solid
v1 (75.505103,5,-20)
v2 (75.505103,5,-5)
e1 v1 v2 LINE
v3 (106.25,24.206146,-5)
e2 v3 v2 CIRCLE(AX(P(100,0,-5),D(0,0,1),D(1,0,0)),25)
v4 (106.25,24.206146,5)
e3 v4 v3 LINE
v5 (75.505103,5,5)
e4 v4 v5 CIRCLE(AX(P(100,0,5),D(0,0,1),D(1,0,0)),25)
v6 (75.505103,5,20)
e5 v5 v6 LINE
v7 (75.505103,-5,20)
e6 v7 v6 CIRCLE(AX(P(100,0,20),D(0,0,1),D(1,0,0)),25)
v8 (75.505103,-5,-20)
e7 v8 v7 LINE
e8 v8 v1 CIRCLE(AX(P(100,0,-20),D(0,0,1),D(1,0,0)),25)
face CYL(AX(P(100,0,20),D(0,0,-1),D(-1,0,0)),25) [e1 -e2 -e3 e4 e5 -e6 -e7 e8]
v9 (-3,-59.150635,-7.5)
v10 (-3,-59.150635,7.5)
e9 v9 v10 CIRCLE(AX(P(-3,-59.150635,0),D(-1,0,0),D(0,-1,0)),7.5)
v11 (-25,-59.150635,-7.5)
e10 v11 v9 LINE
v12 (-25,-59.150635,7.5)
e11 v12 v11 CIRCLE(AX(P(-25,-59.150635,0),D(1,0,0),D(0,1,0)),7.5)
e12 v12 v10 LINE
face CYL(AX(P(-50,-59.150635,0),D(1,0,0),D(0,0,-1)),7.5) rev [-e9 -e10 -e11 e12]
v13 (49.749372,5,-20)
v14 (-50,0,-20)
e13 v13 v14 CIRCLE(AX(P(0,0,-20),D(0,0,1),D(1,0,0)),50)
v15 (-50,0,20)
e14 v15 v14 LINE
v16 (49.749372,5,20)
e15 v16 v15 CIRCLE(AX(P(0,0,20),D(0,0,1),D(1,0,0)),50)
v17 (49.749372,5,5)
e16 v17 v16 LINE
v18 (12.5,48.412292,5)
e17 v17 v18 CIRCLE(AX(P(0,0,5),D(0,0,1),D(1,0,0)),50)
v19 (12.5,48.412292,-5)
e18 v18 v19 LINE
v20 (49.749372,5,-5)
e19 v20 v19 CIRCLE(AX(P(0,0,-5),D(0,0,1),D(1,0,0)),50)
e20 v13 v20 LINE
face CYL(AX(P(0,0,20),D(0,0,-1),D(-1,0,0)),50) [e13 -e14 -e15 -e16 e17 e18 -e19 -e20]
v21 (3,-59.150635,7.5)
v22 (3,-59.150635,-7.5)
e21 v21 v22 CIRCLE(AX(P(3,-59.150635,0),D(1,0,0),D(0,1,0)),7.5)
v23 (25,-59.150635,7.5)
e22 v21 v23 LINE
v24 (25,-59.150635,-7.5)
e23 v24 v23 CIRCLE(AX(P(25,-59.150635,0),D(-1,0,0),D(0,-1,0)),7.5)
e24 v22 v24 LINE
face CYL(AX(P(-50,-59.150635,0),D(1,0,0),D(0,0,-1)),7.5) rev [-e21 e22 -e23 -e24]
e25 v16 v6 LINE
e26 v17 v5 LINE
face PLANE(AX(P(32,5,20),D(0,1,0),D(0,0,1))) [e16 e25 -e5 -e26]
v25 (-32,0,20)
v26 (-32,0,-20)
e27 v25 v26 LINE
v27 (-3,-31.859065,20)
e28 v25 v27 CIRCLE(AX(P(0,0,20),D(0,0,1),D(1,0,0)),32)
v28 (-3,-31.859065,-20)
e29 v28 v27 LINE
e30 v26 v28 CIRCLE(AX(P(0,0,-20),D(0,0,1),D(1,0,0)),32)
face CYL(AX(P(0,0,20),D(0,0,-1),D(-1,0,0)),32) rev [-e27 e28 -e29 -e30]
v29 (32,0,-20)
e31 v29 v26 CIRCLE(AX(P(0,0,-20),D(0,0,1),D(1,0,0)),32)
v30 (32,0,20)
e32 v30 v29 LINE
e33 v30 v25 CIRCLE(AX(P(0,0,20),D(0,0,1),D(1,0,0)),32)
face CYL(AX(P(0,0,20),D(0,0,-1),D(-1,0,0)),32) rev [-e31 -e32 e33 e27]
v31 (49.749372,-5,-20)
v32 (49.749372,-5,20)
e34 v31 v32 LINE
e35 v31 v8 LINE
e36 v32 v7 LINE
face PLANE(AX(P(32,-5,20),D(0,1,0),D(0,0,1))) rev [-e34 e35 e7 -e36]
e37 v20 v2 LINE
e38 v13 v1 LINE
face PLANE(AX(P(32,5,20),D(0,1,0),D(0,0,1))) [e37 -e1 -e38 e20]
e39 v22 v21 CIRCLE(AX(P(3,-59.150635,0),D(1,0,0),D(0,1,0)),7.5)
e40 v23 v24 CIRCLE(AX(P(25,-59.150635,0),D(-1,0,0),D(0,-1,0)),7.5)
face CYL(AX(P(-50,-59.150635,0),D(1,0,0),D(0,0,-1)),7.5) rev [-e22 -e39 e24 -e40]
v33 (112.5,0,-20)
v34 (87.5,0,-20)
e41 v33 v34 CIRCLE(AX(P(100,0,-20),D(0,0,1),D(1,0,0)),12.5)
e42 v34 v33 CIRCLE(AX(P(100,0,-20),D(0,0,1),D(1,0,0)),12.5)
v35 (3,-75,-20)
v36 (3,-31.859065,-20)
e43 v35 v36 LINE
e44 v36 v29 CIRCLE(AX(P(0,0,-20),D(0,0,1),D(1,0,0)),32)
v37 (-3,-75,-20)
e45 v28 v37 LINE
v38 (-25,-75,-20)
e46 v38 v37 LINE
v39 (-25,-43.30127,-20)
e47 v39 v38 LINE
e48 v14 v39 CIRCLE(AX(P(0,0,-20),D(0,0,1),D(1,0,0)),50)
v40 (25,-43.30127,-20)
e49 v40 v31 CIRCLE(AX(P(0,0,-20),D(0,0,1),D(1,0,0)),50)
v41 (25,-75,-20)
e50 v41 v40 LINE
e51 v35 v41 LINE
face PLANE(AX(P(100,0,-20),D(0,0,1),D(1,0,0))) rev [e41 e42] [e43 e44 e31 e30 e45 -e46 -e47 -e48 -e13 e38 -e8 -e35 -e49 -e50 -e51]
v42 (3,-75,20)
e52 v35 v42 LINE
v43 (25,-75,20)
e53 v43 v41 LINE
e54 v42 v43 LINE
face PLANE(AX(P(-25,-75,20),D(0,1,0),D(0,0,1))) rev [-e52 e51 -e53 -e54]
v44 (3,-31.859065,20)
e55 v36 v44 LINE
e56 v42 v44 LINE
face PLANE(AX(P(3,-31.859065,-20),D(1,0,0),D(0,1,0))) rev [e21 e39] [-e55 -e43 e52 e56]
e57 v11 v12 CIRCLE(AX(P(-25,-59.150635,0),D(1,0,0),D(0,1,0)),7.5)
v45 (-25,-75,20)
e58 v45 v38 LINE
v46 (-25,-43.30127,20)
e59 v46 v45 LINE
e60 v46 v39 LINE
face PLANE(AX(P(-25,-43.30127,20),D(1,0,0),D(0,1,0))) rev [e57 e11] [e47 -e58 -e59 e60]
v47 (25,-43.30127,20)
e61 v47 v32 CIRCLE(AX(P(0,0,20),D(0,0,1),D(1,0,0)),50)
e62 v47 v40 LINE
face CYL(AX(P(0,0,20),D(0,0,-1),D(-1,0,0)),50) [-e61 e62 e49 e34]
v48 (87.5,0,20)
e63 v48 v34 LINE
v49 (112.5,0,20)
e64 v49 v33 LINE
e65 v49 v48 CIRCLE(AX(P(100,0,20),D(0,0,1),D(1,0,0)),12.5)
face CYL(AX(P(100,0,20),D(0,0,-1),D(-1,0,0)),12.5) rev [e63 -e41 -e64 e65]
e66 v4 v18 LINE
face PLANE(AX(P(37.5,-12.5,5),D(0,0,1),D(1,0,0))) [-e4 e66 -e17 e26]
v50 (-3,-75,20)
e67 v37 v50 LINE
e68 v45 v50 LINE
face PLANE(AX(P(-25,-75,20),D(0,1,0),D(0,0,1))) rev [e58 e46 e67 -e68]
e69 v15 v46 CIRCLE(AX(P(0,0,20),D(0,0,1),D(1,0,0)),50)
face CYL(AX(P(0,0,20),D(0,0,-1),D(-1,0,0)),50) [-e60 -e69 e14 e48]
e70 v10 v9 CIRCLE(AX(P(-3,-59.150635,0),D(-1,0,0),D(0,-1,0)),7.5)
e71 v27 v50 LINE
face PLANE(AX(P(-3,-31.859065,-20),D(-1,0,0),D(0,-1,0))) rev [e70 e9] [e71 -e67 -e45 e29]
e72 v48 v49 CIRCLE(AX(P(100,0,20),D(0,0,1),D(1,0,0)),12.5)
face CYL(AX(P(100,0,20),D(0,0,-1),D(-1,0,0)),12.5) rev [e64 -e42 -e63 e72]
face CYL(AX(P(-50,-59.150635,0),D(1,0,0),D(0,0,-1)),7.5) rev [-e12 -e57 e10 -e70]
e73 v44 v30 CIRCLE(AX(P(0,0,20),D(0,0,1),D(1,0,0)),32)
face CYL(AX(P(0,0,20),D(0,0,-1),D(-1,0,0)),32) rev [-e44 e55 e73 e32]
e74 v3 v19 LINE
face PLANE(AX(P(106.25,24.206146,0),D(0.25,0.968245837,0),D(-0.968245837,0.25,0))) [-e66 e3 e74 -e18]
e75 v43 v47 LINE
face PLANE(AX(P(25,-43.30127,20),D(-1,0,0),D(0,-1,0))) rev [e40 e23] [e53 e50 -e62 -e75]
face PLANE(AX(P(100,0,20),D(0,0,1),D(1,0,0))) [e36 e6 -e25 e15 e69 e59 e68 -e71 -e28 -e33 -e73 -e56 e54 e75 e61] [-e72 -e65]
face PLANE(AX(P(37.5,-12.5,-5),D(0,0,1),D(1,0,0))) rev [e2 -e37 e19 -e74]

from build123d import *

# Parameters (mm, degrees)
CLAMP_RING_SKETCH_R                       = 50
CLAMP_RING_SKETCH_R_2                     = 32
CLAMP_RING_100_BORE_64_DEPTH              = 20
CLAMP_BLOCK_AND_SECONDARY_BOSS_SKETCH_R   = 25
CLAMP_BLOCK_AND_SECONDARY_BOSS_SKETCH_R_2 = 12.5
CLAMP_BLOCK_AND_SECONDARY_BOSS_SKETCH_W   = 50
CLAMP_BLOCK_AND_SECONDARY_BOSS_SKETCH_H   = 31.698729811
CLAMP_BLOCK_AND_SECONDARY_BOSS_DEPTH      = 20
CLAMP_SLOT_6MM_DEPTH                      = 148.139389696
CLAMP_SLOT_6MM_DEPTH_BACK                 = 148.139389696
CLAMP_SLOT_SKETCH_W                       = 6
CLAMP_SLOT_SKETCH_H                       = 43.140935356
CONNECTING_WEB_SKETCH_W                   = 55.5
CONNECTING_WEB_SKETCH_H                   = 10
CONNECTING_WEB_10MM_DEPTH                 = 20
STIFFENING_RIB_10MM_REACH                 = 149.139
STIFFENING_RIB_SKETCH_WALL_W              = 393.103363046
STIFFENING_RIB_SKETCH_WALL_H              = 10
CLAMP_BOLT_HOLE_15_DEPTH                  = 148.139389696
CLAMP_BOLT_HOLE_15_DEPTH_BACK             = 148.139389696
CLAMP_BOLT_HOLE_SKETCH_R                  = 7.5


with BuildPart() as part:
    # Clamp Ring Sketch → Clamp Ring Ø100 Bore Ø64 (new, symmetric)
    with BuildSketch(Plane.XY):
        Circle(CLAMP_RING_SKETCH_R)
        Circle(CLAMP_RING_SKETCH_R_2, mode=Mode.SUBTRACT)
    extrude(amount=CLAMP_RING_100_BORE_64_DEPTH, both=True)

    # Clamp Block and Secondary Boss Sketch → Clamp Block and Secondary Boss (add, symmetric)
    # profile 1 of 2: a face of its own
    with BuildSketch(Plane.XY):
        with Locations((100, 0)):
            Circle(CLAMP_BLOCK_AND_SECONDARY_BOSS_SKETCH_R)
        with Locations((100, 0)):
            Circle(CLAMP_BLOCK_AND_SECONDARY_BOSS_SKETCH_R_2, mode=Mode.SUBTRACT)
    # profile 2 of 2: a face of its own
    with BuildSketch(Plane.XY):
        with Locations((0, -59.150635095)):
            Rectangle(CLAMP_BLOCK_AND_SECONDARY_BOSS_SKETCH_W, CLAMP_BLOCK_AND_SECONDARY_BOSS_SKETCH_H)
    extrude(amount=CLAMP_BLOCK_AND_SECONDARY_BOSS_DEPTH, both=True)


with BuildPart() as clamp_block_and_secondary_boss_piece_1:
    # of the separate pieces the step leaves, piece 1, a body of its own (clamp_block_and_secondary_boss_pieces)
    add(part.part.solids().sort_by_distance((-25, -43.301270189, 20))[0])

    # Clamp Slot Sketch → Clamp Slot 6mm (cut, two sides: drawn at the far end of the back side and taken through both)
    with BuildSketch(Plane.XY.offset(-CLAMP_SLOT_6MM_DEPTH_BACK)):
        with Locations((0, -53.429532322)):
            Rectangle(CLAMP_SLOT_SKETCH_W, CLAMP_SLOT_SKETCH_H)
    extrude(amount=CLAMP_SLOT_6MM_DEPTH + CLAMP_SLOT_6MM_DEPTH_BACK, mode=Mode.SUBTRACT)



with BuildPart() as clamp_block_and_secondary_boss_piece_2:
    # of the separate pieces the step leaves, piece 2, a body of its own (clamp_block_and_secondary_boss_pieces)
    add(part.part.solids().sort_by_distance((125, 0, -20))[0])


with BuildPart() as clamp_block_and_secondary_boss_piece_1_1:
    add(clamp_block_and_secondary_boss_piece_1.part)

    add(clamp_block_and_secondary_boss_piece_2.part)  # Connecting Web 10mm merges Clamp Block and Secondary Boss piece 2
    # Connecting Web Sketch → Connecting Web 10mm (add, symmetric)
    with BuildSketch(Plane.XY):
        with Locations((59.75, 0)):
            Rectangle(CONNECTING_WEB_SKETCH_W, CONNECTING_WEB_SKETCH_H)
    extrude(amount=CONNECTING_WEB_10MM_DEPTH, both=True)

    # Stiffening Rib Sketch wall → Stiffening Rib 10mm (add, up to next)
    with BuildSketch(Plane(origin=(59.375, 36.309218871, 0), x_dir=(-0.968245836551, 0.250000000002, 0), z_dir=(-0.250000000002, -0.968245836551, 0)), mode=Mode.PRIVATE) as stiffening_rib_10mm_sk1:
        Rectangle(STIFFENING_RIB_SKETCH_WALL_W, STIFFENING_RIB_SKETCH_WALL_H)
    stiffening_rib_10mm_tool1 = extrude(stiffening_rib_10mm_sk1.sketch, amount=STIFFENING_RIB_10MM_REACH, mode=Mode.PRIVATE) - clamp_block_and_secondary_boss_piece_1_1.part
    add(stiffening_rib_10mm_tool1.solids().sort_by_distance((59.375, 36.309218871, 0))[0])

    # Clamp Bolt Hole Sketch → Clamp Bolt Hole Ø15 (cut, two sides: drawn at the far end of the back side and taken through both)
    with BuildSketch(Plane(origin=(0, 0, 0), x_dir=(0, 0, -1), z_dir=(1, 0, 0)).offset(-CLAMP_BOLT_HOLE_15_DEPTH_BACK)):
        with Locations(Location((0, -59.150635095, 0), (0, 0, 270))):
            Circle(CLAMP_BOLT_HOLE_SKETCH_R)
    extrude(amount=CLAMP_BOLT_HOLE_15_DEPTH + CLAMP_BOLT_HOLE_15_DEPTH_BACK, mode=Mode.SUBTRACT)


solid = clamp_block_and_secondary_boss_piece_1_1.part
